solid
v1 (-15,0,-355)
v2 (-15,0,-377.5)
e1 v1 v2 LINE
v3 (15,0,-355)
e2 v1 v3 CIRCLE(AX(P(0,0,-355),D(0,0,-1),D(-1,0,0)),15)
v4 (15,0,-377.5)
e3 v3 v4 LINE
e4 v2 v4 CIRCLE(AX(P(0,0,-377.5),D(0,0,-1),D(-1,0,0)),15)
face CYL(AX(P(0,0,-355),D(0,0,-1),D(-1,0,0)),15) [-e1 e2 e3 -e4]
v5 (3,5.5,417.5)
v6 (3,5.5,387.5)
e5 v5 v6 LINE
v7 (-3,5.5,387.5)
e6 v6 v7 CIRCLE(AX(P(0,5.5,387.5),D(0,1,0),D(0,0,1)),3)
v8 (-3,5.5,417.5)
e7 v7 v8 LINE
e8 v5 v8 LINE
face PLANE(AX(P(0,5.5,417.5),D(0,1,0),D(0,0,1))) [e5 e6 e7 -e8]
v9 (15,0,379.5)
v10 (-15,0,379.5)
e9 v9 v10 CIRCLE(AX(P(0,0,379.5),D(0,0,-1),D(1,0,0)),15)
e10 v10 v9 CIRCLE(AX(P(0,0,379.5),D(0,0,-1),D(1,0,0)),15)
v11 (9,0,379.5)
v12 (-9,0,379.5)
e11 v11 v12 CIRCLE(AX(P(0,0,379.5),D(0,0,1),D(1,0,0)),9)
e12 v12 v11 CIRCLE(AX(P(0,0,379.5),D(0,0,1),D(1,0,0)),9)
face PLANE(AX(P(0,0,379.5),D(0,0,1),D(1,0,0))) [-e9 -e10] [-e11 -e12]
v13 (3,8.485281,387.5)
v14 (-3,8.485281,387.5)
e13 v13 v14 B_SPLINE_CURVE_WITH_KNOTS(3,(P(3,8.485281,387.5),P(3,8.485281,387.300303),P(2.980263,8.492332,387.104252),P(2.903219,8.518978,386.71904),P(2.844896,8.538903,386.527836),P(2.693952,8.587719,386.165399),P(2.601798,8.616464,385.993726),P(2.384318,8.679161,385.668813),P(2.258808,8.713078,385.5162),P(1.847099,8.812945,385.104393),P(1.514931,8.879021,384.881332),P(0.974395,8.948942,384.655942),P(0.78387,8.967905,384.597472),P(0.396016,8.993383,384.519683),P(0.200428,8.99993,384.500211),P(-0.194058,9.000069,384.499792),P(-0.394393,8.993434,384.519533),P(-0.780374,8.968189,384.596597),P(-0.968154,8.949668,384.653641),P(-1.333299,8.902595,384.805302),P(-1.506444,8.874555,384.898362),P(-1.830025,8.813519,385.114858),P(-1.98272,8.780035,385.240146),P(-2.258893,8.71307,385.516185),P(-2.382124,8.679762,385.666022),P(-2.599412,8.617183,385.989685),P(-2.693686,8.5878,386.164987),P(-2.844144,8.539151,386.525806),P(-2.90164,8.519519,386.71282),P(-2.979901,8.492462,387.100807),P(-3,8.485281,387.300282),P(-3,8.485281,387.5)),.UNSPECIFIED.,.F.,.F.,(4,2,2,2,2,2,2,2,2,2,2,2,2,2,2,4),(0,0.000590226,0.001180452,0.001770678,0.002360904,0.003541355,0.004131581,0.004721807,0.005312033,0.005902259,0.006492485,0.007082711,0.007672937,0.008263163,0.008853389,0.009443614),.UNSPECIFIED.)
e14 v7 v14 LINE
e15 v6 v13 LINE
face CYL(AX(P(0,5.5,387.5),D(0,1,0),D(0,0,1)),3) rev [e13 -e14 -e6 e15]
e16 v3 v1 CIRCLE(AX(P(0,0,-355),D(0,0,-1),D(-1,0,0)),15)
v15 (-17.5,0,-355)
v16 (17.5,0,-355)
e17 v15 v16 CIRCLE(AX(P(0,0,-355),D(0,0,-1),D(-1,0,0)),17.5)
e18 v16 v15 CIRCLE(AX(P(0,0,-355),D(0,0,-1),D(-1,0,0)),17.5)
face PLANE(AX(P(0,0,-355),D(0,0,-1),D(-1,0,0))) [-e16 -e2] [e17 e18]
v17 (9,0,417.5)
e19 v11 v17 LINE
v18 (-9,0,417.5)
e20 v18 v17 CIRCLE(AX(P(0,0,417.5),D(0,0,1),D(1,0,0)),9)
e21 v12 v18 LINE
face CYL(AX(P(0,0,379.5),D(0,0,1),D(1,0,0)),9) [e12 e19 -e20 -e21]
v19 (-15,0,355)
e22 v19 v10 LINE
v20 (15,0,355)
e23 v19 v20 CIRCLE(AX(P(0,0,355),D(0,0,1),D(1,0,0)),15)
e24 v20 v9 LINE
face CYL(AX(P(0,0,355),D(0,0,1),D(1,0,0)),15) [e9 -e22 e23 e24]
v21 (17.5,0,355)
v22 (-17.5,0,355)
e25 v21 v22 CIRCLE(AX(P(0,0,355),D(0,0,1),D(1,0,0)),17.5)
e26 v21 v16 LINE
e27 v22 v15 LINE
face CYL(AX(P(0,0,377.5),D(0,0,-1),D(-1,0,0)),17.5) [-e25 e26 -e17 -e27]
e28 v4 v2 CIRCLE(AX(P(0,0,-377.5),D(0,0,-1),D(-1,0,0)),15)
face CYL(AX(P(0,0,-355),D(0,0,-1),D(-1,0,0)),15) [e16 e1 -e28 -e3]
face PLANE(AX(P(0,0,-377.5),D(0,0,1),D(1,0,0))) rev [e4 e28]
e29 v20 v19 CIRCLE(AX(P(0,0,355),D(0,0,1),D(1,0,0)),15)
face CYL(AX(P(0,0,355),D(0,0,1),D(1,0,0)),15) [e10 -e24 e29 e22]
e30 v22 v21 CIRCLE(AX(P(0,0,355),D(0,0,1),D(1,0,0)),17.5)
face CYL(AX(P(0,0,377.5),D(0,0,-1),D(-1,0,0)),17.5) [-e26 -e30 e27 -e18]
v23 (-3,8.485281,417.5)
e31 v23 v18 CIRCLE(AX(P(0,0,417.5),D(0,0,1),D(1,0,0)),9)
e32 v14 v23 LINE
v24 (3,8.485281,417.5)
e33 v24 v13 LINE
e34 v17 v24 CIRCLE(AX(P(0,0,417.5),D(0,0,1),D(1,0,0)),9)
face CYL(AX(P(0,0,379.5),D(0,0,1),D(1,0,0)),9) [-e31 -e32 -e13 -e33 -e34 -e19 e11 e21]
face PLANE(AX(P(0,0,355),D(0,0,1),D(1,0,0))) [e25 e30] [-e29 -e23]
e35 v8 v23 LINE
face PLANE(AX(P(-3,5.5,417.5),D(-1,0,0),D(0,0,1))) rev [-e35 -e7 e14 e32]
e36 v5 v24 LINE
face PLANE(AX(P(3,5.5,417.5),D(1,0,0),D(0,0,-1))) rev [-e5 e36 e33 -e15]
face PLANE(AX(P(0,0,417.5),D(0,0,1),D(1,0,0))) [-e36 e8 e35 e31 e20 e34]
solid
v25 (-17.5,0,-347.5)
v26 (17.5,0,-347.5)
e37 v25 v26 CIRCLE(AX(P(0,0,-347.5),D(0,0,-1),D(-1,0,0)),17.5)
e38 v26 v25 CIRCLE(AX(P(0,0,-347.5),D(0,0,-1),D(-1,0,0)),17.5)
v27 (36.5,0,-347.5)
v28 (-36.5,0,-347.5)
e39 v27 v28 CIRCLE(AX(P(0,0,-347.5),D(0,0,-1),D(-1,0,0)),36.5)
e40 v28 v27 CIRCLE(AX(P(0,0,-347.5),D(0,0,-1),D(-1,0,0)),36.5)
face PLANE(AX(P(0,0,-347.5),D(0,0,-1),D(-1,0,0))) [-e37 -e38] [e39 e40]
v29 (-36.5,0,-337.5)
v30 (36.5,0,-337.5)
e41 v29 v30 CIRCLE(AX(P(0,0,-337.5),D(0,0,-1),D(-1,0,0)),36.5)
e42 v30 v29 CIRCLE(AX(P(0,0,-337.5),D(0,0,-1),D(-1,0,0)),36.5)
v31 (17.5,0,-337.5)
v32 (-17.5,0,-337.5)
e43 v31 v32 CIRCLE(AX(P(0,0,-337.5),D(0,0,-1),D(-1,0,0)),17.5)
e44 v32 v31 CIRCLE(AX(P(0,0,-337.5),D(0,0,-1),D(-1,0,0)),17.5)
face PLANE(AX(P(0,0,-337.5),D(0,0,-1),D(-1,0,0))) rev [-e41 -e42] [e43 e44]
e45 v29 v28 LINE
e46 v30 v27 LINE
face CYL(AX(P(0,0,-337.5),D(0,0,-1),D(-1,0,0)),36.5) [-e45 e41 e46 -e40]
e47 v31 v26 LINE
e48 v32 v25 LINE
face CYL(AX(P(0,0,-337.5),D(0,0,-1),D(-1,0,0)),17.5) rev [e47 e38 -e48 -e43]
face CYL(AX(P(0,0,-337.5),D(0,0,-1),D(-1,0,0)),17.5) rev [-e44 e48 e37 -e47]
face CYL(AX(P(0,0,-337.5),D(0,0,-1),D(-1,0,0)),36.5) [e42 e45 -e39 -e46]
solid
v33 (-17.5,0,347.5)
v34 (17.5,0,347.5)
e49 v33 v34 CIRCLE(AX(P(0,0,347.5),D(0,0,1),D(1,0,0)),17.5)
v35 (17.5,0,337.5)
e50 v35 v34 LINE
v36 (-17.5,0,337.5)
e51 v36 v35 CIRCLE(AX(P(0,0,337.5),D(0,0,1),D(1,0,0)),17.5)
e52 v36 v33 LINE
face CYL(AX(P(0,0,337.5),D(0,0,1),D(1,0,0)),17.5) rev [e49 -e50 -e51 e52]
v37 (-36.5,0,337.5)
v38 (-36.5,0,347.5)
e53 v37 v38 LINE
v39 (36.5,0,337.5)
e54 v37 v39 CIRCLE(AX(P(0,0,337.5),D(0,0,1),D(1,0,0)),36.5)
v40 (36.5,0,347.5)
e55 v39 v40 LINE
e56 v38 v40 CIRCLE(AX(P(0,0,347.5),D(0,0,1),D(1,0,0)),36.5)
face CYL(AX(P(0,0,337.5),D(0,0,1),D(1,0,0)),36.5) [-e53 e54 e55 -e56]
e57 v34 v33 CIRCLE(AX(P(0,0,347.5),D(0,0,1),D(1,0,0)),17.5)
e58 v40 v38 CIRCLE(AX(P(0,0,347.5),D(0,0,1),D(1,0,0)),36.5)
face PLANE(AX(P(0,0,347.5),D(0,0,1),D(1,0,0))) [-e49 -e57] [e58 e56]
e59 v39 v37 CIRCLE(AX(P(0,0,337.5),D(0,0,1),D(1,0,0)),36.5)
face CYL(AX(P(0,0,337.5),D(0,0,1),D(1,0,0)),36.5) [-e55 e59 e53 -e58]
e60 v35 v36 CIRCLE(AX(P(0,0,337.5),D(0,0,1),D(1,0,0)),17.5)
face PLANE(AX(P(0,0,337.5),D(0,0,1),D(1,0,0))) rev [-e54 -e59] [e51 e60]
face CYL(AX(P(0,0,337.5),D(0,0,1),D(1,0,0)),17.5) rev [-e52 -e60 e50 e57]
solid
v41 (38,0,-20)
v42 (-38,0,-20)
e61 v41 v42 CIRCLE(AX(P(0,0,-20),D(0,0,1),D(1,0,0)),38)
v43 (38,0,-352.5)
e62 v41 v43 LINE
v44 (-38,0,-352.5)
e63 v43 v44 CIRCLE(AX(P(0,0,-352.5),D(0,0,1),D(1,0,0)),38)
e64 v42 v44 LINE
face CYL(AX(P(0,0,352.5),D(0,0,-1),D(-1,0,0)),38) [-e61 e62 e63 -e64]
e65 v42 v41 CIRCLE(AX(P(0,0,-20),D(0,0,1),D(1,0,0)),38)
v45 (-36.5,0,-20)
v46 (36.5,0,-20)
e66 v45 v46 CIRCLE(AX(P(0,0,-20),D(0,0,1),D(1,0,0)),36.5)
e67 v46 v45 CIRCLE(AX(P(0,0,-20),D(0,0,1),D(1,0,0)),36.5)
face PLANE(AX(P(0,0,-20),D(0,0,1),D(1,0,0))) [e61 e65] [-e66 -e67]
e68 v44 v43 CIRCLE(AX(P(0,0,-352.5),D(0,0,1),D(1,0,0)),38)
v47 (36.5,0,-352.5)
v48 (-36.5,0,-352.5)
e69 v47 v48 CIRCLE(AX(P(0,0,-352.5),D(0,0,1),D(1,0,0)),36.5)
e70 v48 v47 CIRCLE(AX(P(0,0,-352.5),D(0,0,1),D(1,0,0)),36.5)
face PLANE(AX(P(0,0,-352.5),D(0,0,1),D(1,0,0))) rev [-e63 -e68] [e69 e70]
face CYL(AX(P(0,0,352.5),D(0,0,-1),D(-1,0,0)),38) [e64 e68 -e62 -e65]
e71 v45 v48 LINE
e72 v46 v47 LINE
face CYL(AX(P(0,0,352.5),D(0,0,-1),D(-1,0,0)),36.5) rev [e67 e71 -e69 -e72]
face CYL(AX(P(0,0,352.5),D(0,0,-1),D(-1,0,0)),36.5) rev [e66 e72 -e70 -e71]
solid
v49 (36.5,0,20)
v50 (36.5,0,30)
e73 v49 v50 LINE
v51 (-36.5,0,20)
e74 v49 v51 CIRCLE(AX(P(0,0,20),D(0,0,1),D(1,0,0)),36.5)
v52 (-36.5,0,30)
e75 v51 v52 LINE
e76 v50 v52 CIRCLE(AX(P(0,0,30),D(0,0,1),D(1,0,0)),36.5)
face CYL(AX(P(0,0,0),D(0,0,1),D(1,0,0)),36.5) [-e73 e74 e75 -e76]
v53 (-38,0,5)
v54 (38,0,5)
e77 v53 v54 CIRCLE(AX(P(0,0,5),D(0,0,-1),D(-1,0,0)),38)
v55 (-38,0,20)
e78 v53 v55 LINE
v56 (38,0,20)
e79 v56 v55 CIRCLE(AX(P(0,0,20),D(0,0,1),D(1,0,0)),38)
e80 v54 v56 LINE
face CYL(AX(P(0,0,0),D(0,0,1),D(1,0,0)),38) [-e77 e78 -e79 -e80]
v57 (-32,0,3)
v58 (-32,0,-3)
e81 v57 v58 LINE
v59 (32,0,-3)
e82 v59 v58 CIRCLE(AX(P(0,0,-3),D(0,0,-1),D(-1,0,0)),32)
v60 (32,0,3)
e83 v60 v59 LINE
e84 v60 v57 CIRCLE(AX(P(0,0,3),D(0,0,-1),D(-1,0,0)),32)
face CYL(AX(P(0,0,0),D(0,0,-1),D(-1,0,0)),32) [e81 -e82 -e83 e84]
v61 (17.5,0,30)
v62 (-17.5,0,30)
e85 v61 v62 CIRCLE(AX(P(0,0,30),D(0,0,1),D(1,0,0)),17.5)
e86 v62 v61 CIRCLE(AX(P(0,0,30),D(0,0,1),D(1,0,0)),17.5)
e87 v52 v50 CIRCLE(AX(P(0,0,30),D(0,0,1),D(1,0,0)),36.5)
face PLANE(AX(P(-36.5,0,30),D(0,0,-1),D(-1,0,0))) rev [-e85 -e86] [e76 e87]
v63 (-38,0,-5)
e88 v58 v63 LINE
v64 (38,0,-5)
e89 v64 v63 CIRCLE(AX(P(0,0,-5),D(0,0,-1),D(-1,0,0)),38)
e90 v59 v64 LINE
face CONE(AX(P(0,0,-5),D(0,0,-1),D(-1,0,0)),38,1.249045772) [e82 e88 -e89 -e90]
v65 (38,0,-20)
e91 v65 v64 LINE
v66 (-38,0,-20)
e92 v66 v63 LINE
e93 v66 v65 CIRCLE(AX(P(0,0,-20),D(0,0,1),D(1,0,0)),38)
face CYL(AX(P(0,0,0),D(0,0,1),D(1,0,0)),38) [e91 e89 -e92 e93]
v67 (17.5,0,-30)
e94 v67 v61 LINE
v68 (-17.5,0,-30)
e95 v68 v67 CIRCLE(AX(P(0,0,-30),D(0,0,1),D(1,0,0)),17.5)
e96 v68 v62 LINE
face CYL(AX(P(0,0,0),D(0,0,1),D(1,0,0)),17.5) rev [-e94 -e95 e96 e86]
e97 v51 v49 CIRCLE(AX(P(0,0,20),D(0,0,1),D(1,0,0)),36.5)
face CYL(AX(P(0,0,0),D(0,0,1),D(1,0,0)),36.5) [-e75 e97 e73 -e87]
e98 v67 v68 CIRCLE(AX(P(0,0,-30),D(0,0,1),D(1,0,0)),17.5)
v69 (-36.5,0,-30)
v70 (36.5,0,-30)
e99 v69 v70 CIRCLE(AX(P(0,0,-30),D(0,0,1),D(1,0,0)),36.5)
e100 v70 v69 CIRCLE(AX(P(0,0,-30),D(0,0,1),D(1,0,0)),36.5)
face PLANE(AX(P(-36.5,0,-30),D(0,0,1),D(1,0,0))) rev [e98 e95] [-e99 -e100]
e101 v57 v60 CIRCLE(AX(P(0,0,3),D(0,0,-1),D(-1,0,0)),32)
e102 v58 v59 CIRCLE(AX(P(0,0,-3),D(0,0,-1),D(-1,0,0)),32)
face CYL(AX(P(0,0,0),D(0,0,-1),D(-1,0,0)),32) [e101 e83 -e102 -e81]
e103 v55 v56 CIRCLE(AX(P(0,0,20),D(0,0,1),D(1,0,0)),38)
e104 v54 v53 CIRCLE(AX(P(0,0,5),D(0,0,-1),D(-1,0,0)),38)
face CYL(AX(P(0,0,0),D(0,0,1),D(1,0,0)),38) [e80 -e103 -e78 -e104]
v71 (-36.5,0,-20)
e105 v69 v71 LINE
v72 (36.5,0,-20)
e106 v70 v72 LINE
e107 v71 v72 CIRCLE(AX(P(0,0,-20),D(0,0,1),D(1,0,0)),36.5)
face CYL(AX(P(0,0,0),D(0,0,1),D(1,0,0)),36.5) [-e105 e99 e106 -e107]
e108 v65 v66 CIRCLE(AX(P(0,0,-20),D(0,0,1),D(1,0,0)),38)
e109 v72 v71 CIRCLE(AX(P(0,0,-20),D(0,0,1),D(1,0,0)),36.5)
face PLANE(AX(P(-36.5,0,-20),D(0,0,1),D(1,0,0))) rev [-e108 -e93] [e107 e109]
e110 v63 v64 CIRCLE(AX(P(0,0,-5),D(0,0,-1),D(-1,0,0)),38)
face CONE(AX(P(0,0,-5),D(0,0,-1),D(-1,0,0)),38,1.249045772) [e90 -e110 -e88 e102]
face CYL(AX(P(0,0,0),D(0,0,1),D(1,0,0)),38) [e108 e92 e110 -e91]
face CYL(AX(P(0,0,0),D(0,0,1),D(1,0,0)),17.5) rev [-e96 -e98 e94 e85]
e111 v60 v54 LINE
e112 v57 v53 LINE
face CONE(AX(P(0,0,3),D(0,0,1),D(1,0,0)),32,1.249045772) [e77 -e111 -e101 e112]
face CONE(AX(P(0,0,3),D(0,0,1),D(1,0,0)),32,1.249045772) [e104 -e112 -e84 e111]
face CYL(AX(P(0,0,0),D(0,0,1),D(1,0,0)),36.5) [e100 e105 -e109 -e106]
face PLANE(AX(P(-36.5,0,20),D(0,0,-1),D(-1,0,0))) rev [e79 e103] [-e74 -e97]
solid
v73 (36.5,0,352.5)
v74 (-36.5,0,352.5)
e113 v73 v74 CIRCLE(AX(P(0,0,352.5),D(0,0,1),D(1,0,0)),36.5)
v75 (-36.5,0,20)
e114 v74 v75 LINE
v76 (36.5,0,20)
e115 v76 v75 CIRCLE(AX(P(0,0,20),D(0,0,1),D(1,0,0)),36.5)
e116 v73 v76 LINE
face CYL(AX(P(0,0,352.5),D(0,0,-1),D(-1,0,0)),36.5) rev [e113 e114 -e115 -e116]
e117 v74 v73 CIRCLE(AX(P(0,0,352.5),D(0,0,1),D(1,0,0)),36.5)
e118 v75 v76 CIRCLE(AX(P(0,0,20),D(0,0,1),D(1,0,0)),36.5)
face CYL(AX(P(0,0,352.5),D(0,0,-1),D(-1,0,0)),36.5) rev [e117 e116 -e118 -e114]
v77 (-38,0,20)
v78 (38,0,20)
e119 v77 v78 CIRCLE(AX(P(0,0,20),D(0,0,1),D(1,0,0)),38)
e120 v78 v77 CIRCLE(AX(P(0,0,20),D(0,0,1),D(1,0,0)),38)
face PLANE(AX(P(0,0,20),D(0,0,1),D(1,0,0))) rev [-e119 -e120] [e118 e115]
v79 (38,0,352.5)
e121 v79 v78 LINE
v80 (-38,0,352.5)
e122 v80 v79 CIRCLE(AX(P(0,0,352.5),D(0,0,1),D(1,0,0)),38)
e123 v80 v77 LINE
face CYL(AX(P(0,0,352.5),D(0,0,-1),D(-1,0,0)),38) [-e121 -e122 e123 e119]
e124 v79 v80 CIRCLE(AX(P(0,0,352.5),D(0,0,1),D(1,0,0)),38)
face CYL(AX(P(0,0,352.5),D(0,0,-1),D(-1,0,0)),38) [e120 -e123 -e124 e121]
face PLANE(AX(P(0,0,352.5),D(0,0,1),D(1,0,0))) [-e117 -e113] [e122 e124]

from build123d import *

# Parameters (mm, degrees)
SKETCH_1_R          = 38
SKETCH_1_R_2        = 36.5
EXTRUDE_1_DEPTH     = 352.5
EXTRUDE_START       = -5
SKETCH_2_R          = 36.5
SKETCH_2_R_2        = 17.5
EXTRUDE_2_DEPTH     = 10
SKETCH_3_R          = 36.5
SKETCH_3_R_2        = 17.5
EXTRUDE_3_DEPTH     = 10
SKETCH_10_R         = 17.5
EXTRUDE_4_DEPTH     = 377.5
SKETCH_11_R         = 17.5
EXTRUDE_5_DEPTH     = 40
SKETCH_15_R         = 23.951669513
SKETCH_15_R_2       = 15
CUT_EXTRUDE_2_DEPTH = 62.5
SKETCH_16_R         = 17.5
SKETCH_16_R_2       = 15
CUT_EXTRUDE_3_DEPTH = 22.5
SKETCH_18_R         = 54.962768961
SKETCH_18_R_2       = 24.005660026
CUT_EXTRUDE_4_DEPTH = 20
SKETCH_20_R         = 25
SKETCH_20_R_2       = 9
CUT_EXTRUDE_5_DEPTH = 38
CUT_EXTRUDE_START   = 9
CUT_EXTRUDE_1_DEPTH = 3.5


with BuildPart() as part:
    # 草图1 → 凸台-拉伸1 (new, symmetric)
    with BuildSketch(Plane.XY):
        Circle(SKETCH_1_R)
        Circle(SKETCH_1_R_2, mode=Mode.SUBTRACT)
    extrude(amount=EXTRUDE_1_DEPTH, both=True)

    # 草图18 → 切除-拉伸4 (cut, symmetric)
    with BuildSketch(Plane.XY):
        Circle(SKETCH_18_R)
        Circle(SKETCH_18_R_2, mode=Mode.SUBTRACT)
    extrude(amount=CUT_EXTRUDE_4_DEPTH, both=True, mode=Mode.SUBTRACT)


with BuildPart() as body_2:
    # 草图2 → 凸台-拉伸2 (new body)
    with BuildSketch(Plane.XY.offset(352.5).offset(EXTRUDE_START)):
        Circle(SKETCH_2_R)
        Circle(SKETCH_2_R_2, mode=Mode.SUBTRACT)
    extrude(amount=-EXTRUDE_2_DEPTH)


with BuildPart() as body_3:
    # 草图3 → 凸台-拉伸3 (new body)
    with BuildSketch(Plane(origin=(0, 0, -352.5), x_dir=(-1, 0, 0), z_dir=(0, 0, -1)).offset(EXTRUDE_START)):
        Circle(SKETCH_3_R)
        Circle(SKETCH_3_R_2, mode=Mode.SUBTRACT)
    extrude(amount=-EXTRUDE_3_DEPTH)


with BuildPart() as body_4:
    # 草图10 → 凸台-拉伸4 (new, symmetric)
    with BuildSketch(Plane.XY):
        Circle(SKETCH_10_R)
    extrude(amount=EXTRUDE_4_DEPTH, both=True)

    # 草图11 → 凸台-拉伸5 (add)
    with BuildSketch(Plane.XY.offset(377.5)):
        Circle(SKETCH_11_R)
    extrude(amount=EXTRUDE_5_DEPTH)

    # 草图15 → 切除-拉伸2 (cut)
    with BuildSketch(Plane.XY.offset(417.5)):
        Circle(SKETCH_15_R)
        Circle(SKETCH_15_R_2, mode=Mode.SUBTRACT)
    extrude(amount=-CUT_EXTRUDE_2_DEPTH, mode=Mode.SUBTRACT)

    # 草图16 → 切除-拉伸3 (cut)
    with BuildSketch(Plane(origin=(0, 0, -377.5), x_dir=(-1, 0, 0), z_dir=(0, 0, -1))):
        Circle(SKETCH_16_R)
        with Locations(Location((0, 0, 0), (0, 0, 180))):
            Circle(SKETCH_16_R_2, mode=Mode.SUBTRACT)
    extrude(amount=-CUT_EXTRUDE_3_DEPTH, mode=Mode.SUBTRACT)

    # 草图20 → 切除-拉伸5 (cut)
    with BuildSketch(Plane.XY.offset(417.5)):
        Circle(SKETCH_20_R)
        Circle(SKETCH_20_R_2, mode=Mode.SUBTRACT)
    extrude(amount=-CUT_EXTRUDE_5_DEPTH, mode=Mode.SUBTRACT)

    # 草图14 → 切除-拉伸1 (cut)
    with BuildSketch(Plane(origin=(0, 0, 0), x_dir=(1, 0, 0), z_dir=(0, 1, 0)).offset(CUT_EXTRUDE_START)):
        with BuildLine():
            Line((-3, -417.5), (-3, -387.5))
            ThreePointArc((-3, -387.5), (0, -384.5), (3, -387.5))
            Line((3, -387.5), (3, -417.5))
            ThreePointArc((3, -417.5), (0, -420.5), (-3, -417.5))
        make_face()
    extrude(amount=-CUT_EXTRUDE_1_DEPTH, mode=Mode.SUBTRACT)


with BuildPart() as cut_extrude_4_piece_1:
    # of the separate pieces the step leaves, piece 1, a body of its own (cut_extrude_4_pieces)
    add(part.part.solids().sort_by_distance((38, 0, -352.5))[0])


with BuildPart() as cut_extrude_4_piece_2:
    # of the separate pieces the step leaves, piece 2, a body of its own (cut_extrude_4_pieces)
    add(part.part.solids().sort_by_distance((38, 0, 20))[0])


with BuildPart() as body_6:
    # 草图19 → 旋转2 (revolve)
    with BuildSketch(Plane(origin=(0, 0, 0), x_dir=(1, 0, 0), z_dir=(0, 1, 0)), mode=Mode.PRIVATE) as revolve_2_sk:
        Polygon((-36.5, 30), (-36.5, 20), (-38, 20), (-38, -20), (-36.5, -20), (-36.5, -30), (-17.5, -30), (-17.5, 30), align=None)
    revolve(revolve_2_sk.sketch.rotate(Axis((0, 0, 0), (0, 0, -1)), 180), axis=Axis((0, 0, 0), (0, 0, -1)))

    # 草图17 → 切除-旋转5 (revolve, cut)
    with BuildSketch(Plane(origin=(0, 0, 0), x_dir=(1, 0, 0), z_dir=(0, 1, 0)), mode=Mode.PRIVATE) as cut_revolve_5_sk:
        Polygon((32, 3), (32, -3), (38, -5), (38, 5), align=None)
    revolve(cut_revolve_5_sk.sketch.rotate(Axis((0, 0, 0), (0, 0, 1)), 180), axis=Axis((0, 0, 0), (0, 0, 1)), mode=Mode.SUBTRACT)


solid = Compound([body_2.part, body_3.part, body_4.part, cut_extrude_4_piece_1.part, cut_extrude_4_piece_2.part, body_6.part])
